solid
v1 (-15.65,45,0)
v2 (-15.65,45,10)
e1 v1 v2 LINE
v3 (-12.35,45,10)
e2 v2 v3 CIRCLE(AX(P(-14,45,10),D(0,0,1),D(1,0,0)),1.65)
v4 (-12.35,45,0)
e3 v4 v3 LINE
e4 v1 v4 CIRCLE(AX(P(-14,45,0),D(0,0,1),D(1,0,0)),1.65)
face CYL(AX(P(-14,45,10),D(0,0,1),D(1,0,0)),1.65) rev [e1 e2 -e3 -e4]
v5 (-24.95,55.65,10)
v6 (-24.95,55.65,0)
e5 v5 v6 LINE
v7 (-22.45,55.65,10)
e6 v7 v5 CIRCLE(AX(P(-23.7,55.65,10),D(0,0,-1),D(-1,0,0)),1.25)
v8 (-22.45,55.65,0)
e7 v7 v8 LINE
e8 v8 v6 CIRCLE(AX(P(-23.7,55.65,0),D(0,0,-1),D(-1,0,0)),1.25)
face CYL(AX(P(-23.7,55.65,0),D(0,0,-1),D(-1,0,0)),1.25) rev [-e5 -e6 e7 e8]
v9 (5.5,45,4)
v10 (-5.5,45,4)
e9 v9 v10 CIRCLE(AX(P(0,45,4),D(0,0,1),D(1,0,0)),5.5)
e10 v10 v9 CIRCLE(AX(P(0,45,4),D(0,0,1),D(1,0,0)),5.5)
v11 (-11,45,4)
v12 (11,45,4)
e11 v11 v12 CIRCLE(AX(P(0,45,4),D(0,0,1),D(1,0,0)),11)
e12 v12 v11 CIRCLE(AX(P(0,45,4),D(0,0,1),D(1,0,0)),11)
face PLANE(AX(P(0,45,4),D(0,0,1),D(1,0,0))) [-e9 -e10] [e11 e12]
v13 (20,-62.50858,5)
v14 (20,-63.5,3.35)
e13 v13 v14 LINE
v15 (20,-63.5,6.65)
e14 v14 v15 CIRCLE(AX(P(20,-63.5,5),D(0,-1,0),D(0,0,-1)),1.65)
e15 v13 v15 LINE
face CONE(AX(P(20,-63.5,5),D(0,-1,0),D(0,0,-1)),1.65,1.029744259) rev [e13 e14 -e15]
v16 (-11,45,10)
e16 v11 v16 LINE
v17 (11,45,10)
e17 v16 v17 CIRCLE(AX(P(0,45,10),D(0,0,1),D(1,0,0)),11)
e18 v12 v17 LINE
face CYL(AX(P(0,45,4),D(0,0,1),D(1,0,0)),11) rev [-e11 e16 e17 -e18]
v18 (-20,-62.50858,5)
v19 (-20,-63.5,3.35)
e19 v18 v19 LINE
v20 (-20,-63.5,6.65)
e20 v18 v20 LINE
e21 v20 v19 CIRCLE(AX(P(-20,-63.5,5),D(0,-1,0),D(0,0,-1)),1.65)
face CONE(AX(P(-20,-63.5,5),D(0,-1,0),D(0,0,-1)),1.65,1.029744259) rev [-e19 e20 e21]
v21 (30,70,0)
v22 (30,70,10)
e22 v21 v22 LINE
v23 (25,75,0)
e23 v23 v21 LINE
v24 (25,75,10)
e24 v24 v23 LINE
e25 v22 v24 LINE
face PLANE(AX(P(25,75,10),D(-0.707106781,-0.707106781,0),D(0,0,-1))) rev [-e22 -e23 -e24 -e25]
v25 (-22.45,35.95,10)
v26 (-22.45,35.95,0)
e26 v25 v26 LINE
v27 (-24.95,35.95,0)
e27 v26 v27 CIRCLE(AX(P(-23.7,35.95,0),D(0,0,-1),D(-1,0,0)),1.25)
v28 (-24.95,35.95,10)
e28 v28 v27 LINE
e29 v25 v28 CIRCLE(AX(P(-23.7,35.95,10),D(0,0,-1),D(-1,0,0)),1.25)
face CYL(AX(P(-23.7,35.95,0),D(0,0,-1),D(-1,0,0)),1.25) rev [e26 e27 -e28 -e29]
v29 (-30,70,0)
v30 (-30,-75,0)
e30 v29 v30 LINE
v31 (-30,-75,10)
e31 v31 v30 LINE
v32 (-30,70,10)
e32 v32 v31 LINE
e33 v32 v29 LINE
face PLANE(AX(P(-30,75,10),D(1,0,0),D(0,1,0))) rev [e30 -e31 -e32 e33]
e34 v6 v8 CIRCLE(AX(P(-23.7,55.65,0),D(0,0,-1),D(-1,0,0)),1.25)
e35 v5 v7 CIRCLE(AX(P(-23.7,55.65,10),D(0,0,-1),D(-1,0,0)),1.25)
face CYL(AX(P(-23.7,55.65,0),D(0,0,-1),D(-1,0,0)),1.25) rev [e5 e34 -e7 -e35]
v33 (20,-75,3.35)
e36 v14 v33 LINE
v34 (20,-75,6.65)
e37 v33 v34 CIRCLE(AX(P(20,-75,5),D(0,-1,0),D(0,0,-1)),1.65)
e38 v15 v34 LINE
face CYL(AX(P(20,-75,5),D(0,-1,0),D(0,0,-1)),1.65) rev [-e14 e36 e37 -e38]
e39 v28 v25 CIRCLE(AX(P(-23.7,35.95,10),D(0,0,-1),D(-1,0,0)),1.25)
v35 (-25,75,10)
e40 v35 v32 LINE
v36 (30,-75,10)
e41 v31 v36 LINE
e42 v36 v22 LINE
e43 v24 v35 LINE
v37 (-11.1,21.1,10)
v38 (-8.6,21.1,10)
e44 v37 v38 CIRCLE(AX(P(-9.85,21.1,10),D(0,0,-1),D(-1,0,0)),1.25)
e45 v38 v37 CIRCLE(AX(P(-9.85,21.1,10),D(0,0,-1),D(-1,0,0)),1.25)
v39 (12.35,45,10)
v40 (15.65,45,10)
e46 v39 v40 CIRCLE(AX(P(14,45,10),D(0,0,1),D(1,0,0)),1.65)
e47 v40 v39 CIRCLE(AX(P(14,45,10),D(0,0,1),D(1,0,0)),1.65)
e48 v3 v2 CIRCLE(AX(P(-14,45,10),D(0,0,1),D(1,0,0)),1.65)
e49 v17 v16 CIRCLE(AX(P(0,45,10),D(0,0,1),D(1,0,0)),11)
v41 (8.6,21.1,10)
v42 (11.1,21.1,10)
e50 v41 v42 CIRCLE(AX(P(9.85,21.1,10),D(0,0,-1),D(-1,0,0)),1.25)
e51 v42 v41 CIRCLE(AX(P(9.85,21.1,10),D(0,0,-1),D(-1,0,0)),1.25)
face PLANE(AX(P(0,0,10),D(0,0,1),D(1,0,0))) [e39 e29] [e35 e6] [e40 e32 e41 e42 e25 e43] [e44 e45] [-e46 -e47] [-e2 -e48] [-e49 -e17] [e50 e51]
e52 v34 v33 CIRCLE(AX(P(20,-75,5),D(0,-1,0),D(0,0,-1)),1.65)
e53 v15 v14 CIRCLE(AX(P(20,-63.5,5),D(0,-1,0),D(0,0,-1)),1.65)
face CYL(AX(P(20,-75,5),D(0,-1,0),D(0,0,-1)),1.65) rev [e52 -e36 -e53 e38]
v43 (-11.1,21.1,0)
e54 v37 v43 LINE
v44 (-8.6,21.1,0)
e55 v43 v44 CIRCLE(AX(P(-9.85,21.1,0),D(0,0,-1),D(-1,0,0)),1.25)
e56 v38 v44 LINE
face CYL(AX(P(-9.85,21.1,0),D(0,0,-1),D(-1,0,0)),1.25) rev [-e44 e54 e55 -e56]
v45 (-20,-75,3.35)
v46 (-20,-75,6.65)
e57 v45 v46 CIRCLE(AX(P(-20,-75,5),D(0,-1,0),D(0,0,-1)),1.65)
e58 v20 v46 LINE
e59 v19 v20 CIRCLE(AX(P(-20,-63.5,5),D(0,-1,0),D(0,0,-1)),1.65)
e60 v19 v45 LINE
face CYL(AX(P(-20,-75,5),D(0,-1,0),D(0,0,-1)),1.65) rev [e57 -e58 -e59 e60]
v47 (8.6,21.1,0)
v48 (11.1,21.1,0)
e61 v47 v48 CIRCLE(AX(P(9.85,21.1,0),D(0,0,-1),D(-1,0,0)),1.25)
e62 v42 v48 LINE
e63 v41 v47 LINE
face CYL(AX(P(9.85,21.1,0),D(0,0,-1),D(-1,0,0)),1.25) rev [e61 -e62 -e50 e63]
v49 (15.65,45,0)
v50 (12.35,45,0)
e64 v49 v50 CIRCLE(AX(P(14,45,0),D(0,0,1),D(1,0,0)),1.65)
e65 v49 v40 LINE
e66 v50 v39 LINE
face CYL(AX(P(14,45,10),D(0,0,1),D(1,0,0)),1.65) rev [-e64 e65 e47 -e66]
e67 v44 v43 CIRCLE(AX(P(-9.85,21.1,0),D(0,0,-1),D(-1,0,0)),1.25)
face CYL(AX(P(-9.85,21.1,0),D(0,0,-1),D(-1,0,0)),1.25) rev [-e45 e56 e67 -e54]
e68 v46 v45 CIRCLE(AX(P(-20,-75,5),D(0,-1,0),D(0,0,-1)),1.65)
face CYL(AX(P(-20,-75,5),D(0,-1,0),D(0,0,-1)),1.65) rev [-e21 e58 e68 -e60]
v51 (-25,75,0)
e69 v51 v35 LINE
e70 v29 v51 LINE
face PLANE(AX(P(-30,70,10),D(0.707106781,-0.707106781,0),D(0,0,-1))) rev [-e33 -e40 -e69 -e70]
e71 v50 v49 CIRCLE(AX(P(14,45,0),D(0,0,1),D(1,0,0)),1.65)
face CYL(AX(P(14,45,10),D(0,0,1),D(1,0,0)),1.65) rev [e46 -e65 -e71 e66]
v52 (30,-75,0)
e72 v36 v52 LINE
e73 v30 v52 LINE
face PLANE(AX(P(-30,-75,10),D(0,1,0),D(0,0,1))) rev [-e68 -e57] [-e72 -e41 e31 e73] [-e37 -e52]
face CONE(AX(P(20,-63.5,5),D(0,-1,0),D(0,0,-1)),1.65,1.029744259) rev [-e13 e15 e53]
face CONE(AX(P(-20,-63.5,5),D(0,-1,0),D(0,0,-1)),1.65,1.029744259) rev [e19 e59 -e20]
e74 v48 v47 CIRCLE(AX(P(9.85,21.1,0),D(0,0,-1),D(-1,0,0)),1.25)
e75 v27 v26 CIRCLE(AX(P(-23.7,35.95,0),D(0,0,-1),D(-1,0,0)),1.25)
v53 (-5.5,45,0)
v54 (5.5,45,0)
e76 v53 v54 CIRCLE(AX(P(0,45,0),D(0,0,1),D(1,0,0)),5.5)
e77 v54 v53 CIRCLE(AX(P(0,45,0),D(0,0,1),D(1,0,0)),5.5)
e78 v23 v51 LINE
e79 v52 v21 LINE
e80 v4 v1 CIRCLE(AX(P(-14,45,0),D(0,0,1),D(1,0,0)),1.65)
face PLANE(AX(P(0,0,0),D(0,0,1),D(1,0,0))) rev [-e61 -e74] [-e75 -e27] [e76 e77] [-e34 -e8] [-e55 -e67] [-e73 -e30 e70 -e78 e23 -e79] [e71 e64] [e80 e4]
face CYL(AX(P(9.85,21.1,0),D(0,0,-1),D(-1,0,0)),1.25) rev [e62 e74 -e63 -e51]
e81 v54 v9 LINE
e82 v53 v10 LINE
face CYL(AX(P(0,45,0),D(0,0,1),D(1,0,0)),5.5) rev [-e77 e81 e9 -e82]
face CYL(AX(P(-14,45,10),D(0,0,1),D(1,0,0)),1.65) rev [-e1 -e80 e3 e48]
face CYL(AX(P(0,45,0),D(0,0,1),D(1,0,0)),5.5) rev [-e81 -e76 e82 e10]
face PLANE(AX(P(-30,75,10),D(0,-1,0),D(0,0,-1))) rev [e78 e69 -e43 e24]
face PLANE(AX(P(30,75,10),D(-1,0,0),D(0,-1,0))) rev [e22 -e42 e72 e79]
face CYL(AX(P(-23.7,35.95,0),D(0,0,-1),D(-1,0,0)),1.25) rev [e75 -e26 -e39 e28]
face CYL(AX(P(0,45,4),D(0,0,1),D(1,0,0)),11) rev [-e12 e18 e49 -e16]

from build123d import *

# Parameters (mm, degrees)
SKETCH1_W             = 60
SKETCH1_H             = 150
BOSS_EXTRUDE1_DEPTH   = 10
CHAMFER1_SIZE         = 5
SKETCH2_R             = 11
CUT_EXTRUDE1_DEPTH    = 6
SKETCH3_R             = 5.5
CUT_EXTRUDE2_DEPTH    = 82
M4_TAPPED_HOLE1_D     = 3.3
M4_TAPPED_HOLE2_D     = 3.3
M4_TAPPED_HOLE2_DEPTH = 11.5
M4_TAPPED_HOLE2_TIP   = 0.991420021
M3_TAPPED_HOLE1_D     = 2.5


with BuildPart() as part:
    # Sketch1 → Boss-Extrude1 (new body)
    with BuildSketch(Plane.XY):
        Rectangle(SKETCH1_W, SKETCH1_H)
    extrude(amount=BOSS_EXTRUDE1_DEPTH)

    # Chamfer1
    chamfer1_edges = [part.edges().sort_by_distance(p)[0] for p in [
        (-30, 75, 5),
        (30, 75, 5),
    ]]
    chamfer(chamfer1_edges, length=CHAMFER1_SIZE)

    # Sketch2 → Cut-Extrude1 (cut)
    with BuildSketch(Plane.XY.offset(10)):
        with Locations((0, 45)):
            Circle(SKETCH2_R)
    extrude(amount=-CUT_EXTRUDE1_DEPTH, mode=Mode.SUBTRACT)

    # Sketch3 → Cut-Extrude2 (cut, through all)
    with BuildSketch(Plane.XY.offset(4)):
        with Locations((0, 45)):
            Circle(SKETCH3_R)
    extrude(amount=-CUT_EXTRUDE2_DEPTH, mode=Mode.SUBTRACT)

    # M4 Tapped Hole1 (through all)
    with Locations(Plane.XY.offset(10)):
        with Locations((-14, 45), (14, 45)):
            Hole(M4_TAPPED_HOLE1_D / 2)

    # M4 Tapped Hole2
    with Locations(Plane(origin=(0, -75, 0), x_dir=(-1, 0, 0), z_dir=(0, -1, 0))):
        with Locations((20, -5), (-20, -5)):
            Hole(M4_TAPPED_HOLE2_D / 2, depth=M4_TAPPED_HOLE2_DEPTH)
            with Locations((0, 0, -(M4_TAPPED_HOLE2_DEPTH + M4_TAPPED_HOLE2_TIP / 2))):  # 118° drill point
                Cone(0, M4_TAPPED_HOLE2_D / 2, M4_TAPPED_HOLE2_TIP, mode=Mode.SUBTRACT)

    # M3 Tapped Hole1 (through all)
    with Locations(Plane(origin=(0, 0, 0), x_dir=(-1, 0, 0), z_dir=(0, 0, -1))):
        with Locations((-9.85, 21.1), (9.85, 21.1), (23.7, 35.95), (23.7, 55.65)):
            Hole(M3_TAPPED_HOLE1_D / 2)


solid = part.part
